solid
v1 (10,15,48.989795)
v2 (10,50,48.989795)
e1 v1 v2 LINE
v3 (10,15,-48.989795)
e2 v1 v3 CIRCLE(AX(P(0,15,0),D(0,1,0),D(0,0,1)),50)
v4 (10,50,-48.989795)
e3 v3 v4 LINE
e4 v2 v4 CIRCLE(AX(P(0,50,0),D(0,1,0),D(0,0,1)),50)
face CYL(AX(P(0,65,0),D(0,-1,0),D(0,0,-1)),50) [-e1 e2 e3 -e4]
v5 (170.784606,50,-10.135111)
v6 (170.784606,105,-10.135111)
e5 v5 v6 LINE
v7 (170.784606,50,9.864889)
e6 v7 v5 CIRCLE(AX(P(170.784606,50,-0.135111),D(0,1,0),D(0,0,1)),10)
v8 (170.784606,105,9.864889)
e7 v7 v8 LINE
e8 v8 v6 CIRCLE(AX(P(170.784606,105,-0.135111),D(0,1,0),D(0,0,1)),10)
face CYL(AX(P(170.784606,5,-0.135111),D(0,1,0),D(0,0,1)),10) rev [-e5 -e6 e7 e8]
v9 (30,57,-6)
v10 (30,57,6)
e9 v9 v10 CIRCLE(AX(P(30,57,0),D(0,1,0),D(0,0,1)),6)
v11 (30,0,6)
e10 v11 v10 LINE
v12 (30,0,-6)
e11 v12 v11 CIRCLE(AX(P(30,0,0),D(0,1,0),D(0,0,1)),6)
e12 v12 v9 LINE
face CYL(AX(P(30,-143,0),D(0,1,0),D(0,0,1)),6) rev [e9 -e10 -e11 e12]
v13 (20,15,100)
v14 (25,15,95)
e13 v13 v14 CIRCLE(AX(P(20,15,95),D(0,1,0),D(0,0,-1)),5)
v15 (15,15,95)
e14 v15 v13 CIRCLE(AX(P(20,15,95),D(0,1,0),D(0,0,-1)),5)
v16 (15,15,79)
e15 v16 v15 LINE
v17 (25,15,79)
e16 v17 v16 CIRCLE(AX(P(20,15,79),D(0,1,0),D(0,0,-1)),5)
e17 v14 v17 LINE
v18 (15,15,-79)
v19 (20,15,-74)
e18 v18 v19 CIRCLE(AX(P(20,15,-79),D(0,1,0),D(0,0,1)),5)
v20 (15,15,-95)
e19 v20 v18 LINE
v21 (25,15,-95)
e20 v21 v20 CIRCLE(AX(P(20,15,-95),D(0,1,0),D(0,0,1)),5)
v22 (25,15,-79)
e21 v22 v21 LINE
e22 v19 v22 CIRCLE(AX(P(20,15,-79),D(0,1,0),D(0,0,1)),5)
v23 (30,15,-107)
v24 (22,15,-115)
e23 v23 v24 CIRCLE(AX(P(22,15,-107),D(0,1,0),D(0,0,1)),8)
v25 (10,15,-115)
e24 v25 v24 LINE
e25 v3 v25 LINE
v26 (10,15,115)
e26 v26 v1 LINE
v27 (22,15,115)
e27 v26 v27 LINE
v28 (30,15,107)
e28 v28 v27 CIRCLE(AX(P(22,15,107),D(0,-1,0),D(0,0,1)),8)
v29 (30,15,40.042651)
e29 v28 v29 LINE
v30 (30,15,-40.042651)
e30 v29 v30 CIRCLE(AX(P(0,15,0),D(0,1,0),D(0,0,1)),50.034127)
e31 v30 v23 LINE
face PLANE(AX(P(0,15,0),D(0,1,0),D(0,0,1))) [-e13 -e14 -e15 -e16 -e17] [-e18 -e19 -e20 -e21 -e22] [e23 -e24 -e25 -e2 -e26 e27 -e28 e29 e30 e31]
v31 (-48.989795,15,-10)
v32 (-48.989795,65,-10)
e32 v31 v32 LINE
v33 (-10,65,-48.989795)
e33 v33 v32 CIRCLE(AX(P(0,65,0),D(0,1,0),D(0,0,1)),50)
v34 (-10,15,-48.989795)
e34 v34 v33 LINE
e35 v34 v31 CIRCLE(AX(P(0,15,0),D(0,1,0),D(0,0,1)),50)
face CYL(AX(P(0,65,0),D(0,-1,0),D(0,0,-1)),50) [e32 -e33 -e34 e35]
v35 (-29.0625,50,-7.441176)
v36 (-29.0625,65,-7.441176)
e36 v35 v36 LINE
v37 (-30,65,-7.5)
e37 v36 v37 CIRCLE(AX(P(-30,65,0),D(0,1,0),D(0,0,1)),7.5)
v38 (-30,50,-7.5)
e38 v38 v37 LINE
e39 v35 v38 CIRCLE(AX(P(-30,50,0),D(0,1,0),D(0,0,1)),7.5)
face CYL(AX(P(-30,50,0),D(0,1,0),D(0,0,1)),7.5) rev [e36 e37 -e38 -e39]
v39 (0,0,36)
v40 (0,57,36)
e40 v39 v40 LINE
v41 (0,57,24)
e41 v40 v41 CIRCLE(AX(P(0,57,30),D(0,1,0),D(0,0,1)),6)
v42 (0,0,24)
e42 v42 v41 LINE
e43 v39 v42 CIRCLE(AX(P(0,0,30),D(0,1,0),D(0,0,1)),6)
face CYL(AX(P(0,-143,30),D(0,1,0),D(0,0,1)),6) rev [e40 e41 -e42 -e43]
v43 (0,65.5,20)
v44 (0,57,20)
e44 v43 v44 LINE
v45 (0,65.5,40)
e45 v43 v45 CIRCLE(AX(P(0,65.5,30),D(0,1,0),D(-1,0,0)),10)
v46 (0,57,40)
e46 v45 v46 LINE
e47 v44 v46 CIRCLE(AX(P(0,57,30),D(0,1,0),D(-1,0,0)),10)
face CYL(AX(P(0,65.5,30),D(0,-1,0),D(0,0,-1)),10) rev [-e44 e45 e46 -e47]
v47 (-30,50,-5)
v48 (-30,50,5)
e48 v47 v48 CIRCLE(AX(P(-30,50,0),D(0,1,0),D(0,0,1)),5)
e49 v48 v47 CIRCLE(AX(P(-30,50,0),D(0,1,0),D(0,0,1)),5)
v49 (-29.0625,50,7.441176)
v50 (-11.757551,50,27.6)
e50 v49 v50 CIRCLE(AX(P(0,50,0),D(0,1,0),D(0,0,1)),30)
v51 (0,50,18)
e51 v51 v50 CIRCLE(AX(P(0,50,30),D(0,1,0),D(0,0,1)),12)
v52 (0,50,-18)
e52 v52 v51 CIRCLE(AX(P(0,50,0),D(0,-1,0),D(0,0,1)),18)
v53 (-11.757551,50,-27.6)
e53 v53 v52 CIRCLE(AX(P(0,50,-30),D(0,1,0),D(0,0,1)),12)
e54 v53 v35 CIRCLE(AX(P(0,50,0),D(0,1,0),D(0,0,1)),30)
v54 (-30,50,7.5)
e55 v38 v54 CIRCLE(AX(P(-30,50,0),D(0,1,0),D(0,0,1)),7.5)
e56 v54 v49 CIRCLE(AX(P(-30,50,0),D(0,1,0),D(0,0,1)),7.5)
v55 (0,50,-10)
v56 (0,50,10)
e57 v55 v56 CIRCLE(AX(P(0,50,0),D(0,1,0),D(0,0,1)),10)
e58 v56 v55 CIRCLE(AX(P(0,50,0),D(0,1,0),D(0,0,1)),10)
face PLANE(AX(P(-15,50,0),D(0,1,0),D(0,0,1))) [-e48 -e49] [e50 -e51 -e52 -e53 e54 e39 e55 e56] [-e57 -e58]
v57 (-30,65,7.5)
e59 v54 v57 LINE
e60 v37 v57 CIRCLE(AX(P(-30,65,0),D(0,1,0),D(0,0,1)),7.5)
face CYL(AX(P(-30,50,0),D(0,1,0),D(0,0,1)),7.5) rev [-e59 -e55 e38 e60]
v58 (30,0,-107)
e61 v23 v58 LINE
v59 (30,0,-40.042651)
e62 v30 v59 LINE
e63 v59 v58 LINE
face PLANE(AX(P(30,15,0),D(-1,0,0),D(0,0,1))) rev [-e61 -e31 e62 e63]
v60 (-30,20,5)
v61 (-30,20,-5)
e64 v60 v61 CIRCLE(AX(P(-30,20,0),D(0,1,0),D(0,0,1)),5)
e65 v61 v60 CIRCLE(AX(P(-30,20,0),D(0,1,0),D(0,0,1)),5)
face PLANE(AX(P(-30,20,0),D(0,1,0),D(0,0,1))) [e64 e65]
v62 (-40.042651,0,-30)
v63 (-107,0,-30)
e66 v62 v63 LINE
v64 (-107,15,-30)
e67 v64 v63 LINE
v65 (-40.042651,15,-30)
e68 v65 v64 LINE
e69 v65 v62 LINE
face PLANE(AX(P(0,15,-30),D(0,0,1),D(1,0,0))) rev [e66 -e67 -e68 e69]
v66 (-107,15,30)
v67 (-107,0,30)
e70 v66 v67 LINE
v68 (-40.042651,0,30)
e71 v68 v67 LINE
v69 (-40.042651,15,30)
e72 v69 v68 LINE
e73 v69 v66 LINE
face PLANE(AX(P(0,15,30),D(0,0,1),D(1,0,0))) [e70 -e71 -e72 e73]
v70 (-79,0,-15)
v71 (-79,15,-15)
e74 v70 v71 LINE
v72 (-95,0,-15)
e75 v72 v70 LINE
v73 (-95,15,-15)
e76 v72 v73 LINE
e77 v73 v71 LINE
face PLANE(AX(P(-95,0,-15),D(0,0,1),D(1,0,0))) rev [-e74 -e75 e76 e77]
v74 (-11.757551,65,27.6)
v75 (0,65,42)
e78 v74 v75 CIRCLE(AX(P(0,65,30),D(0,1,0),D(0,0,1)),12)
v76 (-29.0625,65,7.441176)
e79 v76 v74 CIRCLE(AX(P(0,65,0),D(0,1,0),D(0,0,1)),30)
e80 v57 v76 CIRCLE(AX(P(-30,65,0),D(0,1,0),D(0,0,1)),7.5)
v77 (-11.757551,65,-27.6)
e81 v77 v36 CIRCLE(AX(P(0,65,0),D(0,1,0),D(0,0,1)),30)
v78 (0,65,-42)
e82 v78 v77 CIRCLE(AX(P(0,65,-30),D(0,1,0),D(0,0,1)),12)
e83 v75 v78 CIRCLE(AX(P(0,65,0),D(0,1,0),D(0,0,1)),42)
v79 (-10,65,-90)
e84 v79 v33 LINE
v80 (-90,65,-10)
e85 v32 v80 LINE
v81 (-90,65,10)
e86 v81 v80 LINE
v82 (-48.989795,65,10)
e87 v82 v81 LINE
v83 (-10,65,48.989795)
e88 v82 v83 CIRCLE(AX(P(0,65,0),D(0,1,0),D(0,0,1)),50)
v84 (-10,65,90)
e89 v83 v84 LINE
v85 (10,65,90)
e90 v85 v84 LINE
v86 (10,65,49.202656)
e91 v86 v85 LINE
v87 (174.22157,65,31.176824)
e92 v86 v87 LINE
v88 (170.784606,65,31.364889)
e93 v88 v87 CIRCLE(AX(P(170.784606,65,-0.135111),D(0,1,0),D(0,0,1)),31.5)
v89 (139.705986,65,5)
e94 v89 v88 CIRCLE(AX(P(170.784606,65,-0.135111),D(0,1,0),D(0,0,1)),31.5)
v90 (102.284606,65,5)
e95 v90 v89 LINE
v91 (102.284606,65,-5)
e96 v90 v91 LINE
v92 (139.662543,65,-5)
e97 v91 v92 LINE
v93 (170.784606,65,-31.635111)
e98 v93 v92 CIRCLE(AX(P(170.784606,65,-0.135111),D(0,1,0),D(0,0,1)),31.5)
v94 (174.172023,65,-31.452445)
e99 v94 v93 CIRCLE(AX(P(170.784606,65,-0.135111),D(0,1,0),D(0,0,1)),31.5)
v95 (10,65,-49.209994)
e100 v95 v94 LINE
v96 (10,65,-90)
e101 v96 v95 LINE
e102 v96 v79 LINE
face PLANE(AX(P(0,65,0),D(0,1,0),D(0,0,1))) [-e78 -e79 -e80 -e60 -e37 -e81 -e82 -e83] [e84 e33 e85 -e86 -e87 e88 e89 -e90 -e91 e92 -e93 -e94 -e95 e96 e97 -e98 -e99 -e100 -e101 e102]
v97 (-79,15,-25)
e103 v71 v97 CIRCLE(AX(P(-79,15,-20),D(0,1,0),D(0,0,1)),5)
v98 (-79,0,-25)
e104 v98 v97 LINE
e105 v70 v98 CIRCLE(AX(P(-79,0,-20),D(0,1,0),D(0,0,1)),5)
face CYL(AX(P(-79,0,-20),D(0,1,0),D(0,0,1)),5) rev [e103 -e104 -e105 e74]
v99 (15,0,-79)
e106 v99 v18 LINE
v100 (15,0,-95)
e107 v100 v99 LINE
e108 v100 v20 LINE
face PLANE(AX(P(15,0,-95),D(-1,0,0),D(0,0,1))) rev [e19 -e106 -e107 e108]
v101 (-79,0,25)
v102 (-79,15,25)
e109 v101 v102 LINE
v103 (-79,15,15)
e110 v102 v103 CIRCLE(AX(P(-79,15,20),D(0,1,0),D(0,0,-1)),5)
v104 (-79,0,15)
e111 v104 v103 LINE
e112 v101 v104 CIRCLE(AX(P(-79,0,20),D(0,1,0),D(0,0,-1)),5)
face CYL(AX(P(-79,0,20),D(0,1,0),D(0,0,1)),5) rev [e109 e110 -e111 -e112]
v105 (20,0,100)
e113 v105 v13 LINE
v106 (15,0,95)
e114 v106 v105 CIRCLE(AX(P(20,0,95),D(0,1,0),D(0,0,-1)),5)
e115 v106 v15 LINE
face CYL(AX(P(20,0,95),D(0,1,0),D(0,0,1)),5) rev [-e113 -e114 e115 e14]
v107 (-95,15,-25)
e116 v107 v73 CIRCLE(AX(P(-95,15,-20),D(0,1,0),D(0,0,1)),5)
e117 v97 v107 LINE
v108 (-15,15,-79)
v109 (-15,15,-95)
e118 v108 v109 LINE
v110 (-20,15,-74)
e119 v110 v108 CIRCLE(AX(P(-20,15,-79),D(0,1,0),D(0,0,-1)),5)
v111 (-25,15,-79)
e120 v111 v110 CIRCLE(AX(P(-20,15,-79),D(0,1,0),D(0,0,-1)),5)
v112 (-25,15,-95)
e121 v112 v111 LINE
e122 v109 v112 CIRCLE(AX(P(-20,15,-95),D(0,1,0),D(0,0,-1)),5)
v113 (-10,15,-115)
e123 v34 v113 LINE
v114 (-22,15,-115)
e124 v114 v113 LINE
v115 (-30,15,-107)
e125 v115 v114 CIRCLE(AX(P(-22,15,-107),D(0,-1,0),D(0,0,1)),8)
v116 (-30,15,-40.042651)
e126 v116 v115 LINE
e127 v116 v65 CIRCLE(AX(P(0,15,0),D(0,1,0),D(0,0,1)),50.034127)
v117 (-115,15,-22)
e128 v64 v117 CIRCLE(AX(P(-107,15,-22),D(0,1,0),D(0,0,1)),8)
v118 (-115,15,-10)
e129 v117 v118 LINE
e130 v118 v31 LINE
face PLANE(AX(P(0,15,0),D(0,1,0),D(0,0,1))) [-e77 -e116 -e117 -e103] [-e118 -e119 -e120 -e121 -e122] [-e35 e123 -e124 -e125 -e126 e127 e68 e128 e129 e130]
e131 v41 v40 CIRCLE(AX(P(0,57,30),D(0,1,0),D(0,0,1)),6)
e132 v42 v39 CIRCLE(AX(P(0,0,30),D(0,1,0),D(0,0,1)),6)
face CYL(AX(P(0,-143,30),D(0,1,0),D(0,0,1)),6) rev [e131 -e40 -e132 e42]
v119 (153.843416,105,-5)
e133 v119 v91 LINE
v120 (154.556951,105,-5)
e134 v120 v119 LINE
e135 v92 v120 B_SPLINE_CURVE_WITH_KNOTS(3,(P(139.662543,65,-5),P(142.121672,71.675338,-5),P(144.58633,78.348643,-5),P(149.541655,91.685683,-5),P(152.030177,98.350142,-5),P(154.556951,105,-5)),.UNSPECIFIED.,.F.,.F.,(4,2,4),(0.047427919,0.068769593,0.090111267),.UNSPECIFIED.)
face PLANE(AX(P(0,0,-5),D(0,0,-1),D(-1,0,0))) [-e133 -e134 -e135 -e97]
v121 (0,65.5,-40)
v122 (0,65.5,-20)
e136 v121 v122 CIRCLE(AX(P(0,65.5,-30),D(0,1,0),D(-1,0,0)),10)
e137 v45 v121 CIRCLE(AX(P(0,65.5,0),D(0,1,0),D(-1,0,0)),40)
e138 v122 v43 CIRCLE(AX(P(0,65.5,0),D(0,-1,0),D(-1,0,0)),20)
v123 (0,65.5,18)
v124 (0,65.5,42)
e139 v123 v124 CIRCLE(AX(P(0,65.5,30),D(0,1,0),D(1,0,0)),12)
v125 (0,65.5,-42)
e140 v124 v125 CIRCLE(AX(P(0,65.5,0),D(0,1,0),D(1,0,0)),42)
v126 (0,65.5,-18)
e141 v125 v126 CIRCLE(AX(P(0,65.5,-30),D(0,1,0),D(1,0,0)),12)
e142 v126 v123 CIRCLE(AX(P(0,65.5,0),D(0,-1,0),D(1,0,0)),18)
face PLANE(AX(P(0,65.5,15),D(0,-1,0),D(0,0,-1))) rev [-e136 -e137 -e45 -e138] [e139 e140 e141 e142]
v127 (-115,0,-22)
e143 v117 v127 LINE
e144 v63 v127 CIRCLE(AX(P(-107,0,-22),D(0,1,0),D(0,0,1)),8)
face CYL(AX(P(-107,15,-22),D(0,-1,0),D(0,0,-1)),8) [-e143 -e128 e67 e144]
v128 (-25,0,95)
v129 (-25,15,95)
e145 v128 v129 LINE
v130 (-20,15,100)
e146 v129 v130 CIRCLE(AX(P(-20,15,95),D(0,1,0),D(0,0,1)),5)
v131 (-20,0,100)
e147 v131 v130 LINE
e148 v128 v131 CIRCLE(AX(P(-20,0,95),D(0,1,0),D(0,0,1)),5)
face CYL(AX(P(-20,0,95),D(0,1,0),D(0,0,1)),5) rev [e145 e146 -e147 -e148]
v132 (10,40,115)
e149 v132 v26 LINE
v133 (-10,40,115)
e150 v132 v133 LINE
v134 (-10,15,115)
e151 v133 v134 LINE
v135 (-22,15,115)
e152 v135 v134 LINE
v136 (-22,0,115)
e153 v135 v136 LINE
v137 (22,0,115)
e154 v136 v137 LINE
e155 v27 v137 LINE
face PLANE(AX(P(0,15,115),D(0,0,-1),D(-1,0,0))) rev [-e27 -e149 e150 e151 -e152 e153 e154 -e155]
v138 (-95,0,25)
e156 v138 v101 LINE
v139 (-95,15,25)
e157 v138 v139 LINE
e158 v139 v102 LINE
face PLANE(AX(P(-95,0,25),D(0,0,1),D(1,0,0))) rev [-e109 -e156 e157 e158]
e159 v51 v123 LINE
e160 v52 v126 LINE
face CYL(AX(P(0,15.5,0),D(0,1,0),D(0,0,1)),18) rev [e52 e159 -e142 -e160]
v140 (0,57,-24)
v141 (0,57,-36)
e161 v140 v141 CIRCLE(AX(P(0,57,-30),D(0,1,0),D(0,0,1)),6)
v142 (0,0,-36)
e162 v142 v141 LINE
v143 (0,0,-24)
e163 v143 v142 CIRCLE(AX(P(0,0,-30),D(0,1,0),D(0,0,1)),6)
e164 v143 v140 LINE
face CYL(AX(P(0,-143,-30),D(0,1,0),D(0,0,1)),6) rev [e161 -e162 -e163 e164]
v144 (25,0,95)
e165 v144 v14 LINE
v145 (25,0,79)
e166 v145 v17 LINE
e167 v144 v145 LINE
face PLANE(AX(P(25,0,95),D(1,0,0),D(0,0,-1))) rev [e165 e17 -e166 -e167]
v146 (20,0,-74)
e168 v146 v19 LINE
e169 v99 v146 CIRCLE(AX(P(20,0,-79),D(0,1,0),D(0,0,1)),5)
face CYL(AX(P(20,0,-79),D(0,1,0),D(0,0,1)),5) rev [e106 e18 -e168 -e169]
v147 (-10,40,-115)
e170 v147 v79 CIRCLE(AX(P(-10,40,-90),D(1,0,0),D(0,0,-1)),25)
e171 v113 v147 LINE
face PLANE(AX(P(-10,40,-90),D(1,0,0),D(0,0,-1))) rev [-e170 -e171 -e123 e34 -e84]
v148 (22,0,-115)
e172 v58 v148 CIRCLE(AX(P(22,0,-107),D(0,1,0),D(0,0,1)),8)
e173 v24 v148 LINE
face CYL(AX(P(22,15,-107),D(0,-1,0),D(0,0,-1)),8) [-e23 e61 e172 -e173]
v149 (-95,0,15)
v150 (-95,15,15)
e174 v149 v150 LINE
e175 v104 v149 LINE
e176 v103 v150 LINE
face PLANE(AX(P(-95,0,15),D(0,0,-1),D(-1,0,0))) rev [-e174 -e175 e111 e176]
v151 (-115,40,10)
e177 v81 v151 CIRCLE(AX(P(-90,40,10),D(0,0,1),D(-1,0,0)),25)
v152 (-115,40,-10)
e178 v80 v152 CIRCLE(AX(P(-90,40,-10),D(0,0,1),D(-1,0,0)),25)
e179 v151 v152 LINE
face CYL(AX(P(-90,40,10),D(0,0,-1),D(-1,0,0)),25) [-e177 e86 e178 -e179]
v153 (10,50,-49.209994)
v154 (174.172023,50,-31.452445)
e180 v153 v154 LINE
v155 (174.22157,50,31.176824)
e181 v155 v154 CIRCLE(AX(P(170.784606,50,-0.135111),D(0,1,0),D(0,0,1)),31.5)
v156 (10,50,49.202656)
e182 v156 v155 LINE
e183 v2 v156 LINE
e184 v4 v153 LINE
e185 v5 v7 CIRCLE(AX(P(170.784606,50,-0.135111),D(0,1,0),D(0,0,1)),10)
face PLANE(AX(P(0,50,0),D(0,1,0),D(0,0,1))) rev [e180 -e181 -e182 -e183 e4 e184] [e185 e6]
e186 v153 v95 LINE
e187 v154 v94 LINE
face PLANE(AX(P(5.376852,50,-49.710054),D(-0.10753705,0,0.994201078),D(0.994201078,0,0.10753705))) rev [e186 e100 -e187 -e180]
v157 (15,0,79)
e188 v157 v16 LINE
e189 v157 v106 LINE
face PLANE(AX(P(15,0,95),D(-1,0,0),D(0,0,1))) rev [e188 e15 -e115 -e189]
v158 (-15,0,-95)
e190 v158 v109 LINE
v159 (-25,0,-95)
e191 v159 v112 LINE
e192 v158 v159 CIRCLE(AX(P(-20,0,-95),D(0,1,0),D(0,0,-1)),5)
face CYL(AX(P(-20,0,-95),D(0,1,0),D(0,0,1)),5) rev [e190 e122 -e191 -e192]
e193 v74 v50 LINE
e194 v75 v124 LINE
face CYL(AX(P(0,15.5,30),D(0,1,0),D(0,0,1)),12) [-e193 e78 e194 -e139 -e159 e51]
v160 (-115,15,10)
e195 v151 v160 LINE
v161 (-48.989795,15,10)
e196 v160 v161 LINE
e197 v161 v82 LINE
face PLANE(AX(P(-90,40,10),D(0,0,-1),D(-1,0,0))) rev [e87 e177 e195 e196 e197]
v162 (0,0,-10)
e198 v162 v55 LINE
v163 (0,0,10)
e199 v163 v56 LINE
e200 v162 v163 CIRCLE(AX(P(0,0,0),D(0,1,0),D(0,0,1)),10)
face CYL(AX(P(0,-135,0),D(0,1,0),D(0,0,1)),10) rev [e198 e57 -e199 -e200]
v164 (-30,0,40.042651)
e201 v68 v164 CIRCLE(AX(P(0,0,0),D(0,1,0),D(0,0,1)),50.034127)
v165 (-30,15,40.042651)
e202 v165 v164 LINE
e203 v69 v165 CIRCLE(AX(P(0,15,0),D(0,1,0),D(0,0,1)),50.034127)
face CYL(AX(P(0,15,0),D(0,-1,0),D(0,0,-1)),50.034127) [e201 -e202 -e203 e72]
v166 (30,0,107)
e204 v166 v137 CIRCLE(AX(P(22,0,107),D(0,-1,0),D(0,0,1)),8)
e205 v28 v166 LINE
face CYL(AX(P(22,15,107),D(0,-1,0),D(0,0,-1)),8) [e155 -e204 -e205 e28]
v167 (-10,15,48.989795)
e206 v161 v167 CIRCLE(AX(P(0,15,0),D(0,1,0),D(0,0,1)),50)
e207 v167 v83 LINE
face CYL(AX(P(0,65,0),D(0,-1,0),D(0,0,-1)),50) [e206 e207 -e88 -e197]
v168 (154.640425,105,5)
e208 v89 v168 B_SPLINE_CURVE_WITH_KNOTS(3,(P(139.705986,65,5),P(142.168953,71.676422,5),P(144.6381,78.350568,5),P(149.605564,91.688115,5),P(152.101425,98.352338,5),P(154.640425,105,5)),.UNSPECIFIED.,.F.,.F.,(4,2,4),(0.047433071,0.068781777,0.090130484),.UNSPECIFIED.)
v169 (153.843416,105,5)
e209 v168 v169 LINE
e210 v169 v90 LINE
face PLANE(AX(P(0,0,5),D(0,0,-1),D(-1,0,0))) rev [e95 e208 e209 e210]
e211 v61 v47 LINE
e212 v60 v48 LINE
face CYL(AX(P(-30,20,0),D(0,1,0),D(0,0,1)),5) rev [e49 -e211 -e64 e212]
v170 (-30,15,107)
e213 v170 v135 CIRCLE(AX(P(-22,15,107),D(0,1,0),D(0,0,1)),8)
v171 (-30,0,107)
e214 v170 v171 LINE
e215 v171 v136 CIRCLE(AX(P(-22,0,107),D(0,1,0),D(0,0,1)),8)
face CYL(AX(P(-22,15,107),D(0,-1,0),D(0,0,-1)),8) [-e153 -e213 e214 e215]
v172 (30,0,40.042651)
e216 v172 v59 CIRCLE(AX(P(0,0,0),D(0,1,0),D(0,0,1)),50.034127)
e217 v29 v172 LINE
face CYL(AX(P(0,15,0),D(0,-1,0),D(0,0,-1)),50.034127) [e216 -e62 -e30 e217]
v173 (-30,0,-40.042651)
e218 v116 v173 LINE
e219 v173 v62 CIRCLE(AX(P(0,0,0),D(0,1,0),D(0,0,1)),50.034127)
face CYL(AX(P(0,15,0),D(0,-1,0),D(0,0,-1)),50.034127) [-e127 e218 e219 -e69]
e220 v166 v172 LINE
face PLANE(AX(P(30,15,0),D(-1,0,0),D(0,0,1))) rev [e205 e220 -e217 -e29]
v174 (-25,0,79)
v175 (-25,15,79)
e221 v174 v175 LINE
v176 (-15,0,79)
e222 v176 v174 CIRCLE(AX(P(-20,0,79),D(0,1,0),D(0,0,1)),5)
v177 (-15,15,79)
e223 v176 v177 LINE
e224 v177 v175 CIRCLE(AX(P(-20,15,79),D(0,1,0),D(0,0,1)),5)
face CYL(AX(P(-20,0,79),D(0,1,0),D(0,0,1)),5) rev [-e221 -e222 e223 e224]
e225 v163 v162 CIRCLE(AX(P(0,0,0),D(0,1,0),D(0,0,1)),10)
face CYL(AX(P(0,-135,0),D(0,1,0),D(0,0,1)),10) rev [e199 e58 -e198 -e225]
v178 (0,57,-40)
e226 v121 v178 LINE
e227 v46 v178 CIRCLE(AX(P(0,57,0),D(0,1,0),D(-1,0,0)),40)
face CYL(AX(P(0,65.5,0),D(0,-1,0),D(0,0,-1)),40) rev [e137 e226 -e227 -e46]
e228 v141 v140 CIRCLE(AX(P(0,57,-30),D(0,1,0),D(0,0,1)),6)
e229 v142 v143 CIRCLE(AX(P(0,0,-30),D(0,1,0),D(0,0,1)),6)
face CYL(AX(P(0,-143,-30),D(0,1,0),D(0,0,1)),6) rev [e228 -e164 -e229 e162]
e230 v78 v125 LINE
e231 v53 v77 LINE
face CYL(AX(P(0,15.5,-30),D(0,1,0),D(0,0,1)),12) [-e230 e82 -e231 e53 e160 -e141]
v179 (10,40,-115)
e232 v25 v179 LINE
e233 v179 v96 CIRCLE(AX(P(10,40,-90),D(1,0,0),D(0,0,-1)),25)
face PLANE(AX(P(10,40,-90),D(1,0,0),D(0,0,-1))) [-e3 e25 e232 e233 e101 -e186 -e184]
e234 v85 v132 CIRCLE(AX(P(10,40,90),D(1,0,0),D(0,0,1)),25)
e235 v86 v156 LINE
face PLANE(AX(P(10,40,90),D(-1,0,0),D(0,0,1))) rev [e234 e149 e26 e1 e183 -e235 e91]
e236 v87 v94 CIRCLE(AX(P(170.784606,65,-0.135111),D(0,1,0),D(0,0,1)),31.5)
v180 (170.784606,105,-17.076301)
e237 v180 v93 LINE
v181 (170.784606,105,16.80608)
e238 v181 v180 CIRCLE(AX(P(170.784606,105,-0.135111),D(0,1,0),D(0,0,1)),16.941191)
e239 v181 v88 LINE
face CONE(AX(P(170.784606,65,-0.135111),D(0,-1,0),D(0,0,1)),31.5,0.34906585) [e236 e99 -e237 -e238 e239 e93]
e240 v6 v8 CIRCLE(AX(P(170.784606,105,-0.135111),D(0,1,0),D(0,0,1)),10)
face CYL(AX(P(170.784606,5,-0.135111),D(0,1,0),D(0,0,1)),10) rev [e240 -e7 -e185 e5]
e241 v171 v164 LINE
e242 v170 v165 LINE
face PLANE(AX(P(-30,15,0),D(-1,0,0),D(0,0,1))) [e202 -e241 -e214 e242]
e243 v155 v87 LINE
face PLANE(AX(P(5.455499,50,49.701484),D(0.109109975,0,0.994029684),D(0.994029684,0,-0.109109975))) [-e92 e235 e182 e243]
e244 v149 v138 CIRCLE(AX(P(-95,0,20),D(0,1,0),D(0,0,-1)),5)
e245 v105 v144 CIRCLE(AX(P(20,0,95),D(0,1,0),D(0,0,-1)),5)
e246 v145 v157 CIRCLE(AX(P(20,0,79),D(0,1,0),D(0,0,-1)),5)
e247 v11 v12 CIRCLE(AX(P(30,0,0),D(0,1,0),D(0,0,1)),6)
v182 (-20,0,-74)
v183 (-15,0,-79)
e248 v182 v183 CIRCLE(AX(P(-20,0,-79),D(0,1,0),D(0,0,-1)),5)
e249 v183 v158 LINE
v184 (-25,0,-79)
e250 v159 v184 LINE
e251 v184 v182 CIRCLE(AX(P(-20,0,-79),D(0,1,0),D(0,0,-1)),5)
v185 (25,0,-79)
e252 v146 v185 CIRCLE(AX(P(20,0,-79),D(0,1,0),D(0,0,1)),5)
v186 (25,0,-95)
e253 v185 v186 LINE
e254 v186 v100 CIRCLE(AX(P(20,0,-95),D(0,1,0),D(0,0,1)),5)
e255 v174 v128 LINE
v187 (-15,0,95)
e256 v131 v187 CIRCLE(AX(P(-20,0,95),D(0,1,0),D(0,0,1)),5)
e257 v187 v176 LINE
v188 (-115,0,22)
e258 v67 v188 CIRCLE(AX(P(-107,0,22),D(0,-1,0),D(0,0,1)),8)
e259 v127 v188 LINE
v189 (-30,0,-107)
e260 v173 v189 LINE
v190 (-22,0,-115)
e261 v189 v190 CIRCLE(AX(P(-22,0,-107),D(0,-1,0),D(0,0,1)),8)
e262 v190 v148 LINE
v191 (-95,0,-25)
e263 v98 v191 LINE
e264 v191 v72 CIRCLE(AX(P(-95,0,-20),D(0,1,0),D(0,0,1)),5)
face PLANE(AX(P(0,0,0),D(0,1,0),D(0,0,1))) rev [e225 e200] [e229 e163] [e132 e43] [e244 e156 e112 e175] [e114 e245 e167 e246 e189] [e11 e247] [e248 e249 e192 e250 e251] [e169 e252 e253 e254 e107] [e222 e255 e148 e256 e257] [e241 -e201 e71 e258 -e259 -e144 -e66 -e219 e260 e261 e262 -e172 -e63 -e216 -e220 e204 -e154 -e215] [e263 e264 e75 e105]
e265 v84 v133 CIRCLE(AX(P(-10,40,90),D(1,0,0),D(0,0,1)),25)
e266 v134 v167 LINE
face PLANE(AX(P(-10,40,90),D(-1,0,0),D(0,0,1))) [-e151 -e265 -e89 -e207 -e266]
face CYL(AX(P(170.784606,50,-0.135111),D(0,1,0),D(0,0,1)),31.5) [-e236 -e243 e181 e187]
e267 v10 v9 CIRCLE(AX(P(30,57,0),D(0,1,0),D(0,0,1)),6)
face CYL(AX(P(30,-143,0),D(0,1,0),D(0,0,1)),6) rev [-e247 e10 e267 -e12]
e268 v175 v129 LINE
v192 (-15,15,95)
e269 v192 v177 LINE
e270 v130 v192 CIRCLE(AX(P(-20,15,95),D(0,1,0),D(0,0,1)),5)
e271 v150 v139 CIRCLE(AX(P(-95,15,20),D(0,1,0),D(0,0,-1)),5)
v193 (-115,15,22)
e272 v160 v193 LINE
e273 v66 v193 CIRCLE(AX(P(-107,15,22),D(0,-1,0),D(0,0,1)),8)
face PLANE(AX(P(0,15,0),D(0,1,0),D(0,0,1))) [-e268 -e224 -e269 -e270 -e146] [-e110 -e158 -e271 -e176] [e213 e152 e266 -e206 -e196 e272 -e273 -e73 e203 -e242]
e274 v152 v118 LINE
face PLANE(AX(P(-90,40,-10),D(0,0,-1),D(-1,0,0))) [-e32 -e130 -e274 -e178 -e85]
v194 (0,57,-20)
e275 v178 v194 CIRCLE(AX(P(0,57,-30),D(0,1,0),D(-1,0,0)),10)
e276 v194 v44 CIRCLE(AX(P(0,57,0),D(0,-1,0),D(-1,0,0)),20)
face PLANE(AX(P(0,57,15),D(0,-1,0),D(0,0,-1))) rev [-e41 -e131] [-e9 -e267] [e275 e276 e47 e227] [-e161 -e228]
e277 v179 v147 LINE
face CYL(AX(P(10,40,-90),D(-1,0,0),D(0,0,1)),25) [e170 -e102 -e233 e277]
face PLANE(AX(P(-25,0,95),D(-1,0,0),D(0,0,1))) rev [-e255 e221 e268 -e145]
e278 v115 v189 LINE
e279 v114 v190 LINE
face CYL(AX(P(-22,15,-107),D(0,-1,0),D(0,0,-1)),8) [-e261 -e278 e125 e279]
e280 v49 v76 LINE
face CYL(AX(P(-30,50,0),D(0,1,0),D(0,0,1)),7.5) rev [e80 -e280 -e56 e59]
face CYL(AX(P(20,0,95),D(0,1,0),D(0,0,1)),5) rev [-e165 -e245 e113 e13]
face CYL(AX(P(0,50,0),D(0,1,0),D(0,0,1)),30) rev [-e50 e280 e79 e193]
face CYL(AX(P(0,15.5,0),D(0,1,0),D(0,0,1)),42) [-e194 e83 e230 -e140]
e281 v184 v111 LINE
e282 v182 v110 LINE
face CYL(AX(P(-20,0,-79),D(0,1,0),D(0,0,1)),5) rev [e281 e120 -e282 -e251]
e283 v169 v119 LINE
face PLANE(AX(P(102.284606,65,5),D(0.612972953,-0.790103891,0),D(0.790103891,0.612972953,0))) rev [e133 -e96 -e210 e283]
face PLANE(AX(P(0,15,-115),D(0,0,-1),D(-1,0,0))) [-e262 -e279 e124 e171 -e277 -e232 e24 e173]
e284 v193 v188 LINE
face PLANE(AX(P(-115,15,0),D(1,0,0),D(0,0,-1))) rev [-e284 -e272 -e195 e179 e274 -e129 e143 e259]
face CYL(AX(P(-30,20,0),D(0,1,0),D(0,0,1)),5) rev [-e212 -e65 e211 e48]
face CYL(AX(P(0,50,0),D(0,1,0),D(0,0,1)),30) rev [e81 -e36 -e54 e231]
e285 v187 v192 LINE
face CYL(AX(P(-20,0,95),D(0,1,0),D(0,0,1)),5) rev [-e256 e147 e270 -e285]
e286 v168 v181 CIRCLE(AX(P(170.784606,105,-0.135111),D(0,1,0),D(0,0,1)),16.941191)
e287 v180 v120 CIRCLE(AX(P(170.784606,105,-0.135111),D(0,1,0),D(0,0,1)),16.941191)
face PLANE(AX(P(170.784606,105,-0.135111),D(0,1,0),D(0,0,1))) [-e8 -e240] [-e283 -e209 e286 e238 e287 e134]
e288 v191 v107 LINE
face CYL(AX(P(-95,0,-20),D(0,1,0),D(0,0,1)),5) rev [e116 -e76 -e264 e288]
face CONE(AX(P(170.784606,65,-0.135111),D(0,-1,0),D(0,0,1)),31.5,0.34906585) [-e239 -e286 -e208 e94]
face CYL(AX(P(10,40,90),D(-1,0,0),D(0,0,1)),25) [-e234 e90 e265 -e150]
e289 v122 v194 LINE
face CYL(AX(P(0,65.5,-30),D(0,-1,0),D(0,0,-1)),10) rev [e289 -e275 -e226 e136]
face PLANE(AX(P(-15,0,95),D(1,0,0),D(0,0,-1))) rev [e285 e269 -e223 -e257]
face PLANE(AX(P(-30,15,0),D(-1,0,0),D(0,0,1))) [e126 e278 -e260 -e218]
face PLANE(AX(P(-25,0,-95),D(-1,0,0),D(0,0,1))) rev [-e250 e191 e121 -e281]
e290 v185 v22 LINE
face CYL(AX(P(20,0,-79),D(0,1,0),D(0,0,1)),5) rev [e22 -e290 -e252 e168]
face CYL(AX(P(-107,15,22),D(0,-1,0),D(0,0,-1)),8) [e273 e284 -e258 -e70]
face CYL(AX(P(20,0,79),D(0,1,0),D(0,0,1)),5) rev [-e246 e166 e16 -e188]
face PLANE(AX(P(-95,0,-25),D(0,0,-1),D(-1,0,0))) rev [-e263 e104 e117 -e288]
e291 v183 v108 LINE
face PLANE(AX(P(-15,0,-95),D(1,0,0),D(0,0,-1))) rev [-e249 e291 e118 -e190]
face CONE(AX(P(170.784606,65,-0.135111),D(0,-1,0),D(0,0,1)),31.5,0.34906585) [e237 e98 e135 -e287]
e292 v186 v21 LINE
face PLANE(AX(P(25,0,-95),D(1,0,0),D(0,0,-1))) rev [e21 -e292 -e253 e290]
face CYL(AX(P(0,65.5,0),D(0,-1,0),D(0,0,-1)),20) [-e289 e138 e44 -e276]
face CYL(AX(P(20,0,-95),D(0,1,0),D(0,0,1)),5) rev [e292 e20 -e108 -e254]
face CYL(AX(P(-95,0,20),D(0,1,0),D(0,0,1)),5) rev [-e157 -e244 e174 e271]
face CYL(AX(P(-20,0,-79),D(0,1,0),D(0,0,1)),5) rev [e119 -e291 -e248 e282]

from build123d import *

# Parameters (mm, degrees)
CROSS_BASE_PLATE_SKETCH_R    = 50.034127187
CROSS_BASE_PLATE_DEPTH       = 15
ARM_SLOTS_DEPTH              = 15
CENTRAL_HUB_SKETCH_R         = 50
CENTRAL_HUB_100_DEPTH        = 50
TRUNNION_START               = -15
TRUNNION_ARM_PLATE_DEPTH     = 15
TRUNNION_CONE_SKETCH_R       = 31.5
TRUNNION_CONE_BOSS_DEPTH     = 40
TRUNNION_CONE_BOSS_TAPER     = 20
TRUNNION_BORE_SKETCH_R       = 10
TRUNNION_BORE_20_DEPTH       = 100
TRUNNION_GUSSET_DEPTH        = 5
ARM_UPRIGHT_BLOCK_DEPTH      = 10
ARM_UPRIGHT_BLOCK_PAIR_DEPTH = 10
CENTRAL_BORE_SKETCH_R        = 10
CENTRAL_BORE_20_DEPTH        = 200
HUB_TOP_RECESS_SKETCH_R      = 10
HUB_TOP_RECESS_DEPTH         = 15
HUB_LOBE_POCKET_DEPTH        = 8
POCKET_FLOOR_PAD_DEPTH       = 1
POCKET_START                 = 8.5
POCKET_THIN_WALL_DEPTH       = 8.5
HUB_PIN_HOLES_SKETCH_R       = 6
HUB_PIN_HOLES_DEPTH          = 200
POCKET_OUTER_WALL_DEPTH      = 50
PIN_HOLE_BOSSES_SKETCH_R     = 6
PIN_HOLE_BOSSES_DEPTH        = 20
HUB_SIDE_HOLE_SKETCH_R       = 5
HUB_SIDE_HOLE_10_DEPTH       = 30


with BuildPart() as part:
    # Cross Base Plate Sketch → Cross Base Plate (new body)
    with BuildSketch(Plane(origin=(0, 0, 0), x_dir=(1, 0, 0), z_dir=(0, 1, 0))):
        with BuildLine():
            ThreePointArc((-40.042650803, -30), (-50.034127187, 0), (-40.042650803, 30))
            Line((-40.042650803, 30), (-107, 30))
            ThreePointArc((-107, 30), (-112.656854249, 27.656854249), (-115, 22))
            Line((-115, 22), (-115, -22))
            ThreePointArc((-115, -22), (-112.656854249, -27.656854249), (-107, -30))
            Line((-107, -30), (-40.042650803, -30))
        make_face()
        Circle(CROSS_BASE_PLATE_SKETCH_R)
        with BuildLine():
            ThreePointArc((-30, 40.042650803), (0, 50.034127187), (30, 40.042650803))
            Line((30, 40.042650803), (30, 107))
            ThreePointArc((30, 107), (27.656854249, 112.656854249), (22, 115))
            Line((22, 115), (-22, 115))
            ThreePointArc((-22, 115), (-27.656854249, 112.656854249), (-30, 107))
            Line((-30, 107), (-30, 40.042650803))
        make_face()
        with BuildLine():
            Line((30, -107), (30, -40.042650803))
            ThreePointArc((30, -40.042650803), (0, -50.034127187), (-30, -40.042650803))
            Line((-30, -40.042650803), (-30, -107))
            ThreePointArc((-30, -107), (-27.656854249, -112.656854249), (-22, -115))
            Line((-22, -115), (22, -115))
            ThreePointArc((22, -115), (27.656854249, -112.656854249), (30, -107))
        make_face()
    extrude(amount=CROSS_BASE_PLATE_DEPTH)

    # Arm Slots Sketch → Arm Slots (cut)
    with BuildSketch(Plane(origin=(0, 15, 0), x_dir=(1, 0, 0), z_dir=(0, 1, 0))):
        with BuildLine():
            Line((-95, 25), (-79, 25))
            ThreePointArc((-79, 25), (-74, 20), (-79, 15))
            Line((-79, 15), (-95, 15))
            ThreePointArc((-95, 15), (-100, 20), (-95, 25))
        make_face()
        with BuildLine():
            Line((-95, -25), (-79, -25))
            ThreePointArc((-79, -25), (-74, -20), (-79, -15))
            Line((-79, -15), (-95, -15))
            ThreePointArc((-95, -15), (-100, -20), (-95, -25))
        make_face()
        with BuildLine():
            Line((25, 95), (25, 79))
            ThreePointArc((25, 79), (20, 74), (15, 79))
            Line((15, 79), (15, 95))
            ThreePointArc((15, 95), (20, 100), (25, 95))
        make_face()
        with BuildLine():
            Line((-25, 95), (-25, 79))
            ThreePointArc((-25, 79), (-20, 74), (-15, 79))
            Line((-15, 79), (-15, 95))
            ThreePointArc((-15, 95), (-20, 100), (-25, 95))
        make_face()
        with BuildLine():
            Line((25, -95), (25, -79))
            ThreePointArc((25, -79), (20, -74), (15, -79))
            Line((15, -79), (15, -95))
            ThreePointArc((15, -95), (20, -100), (25, -95))
        make_face()
        with BuildLine():
            Line((-25, -95), (-25, -79))
            ThreePointArc((-25, -79), (-20, -74), (-15, -79))
            Line((-15, -79), (-15, -95))
            ThreePointArc((-15, -95), (-20, -100), (-25, -95))
        make_face()
    extrude(amount=-ARM_SLOTS_DEPTH, mode=Mode.SUBTRACT)

    # Central Hub Sketch → Central Hub Ø100 (add)
    with BuildSketch(Plane(origin=(0, 15, 0), x_dir=(1, 0, 0), z_dir=(0, 1, 0))):
        with Locations(Location((0, 0, 0), (0, 0, 270))):
            Circle(CENTRAL_HUB_SKETCH_R)
    extrude(amount=CENTRAL_HUB_100_DEPTH)

    # Trunnion Arm Plate Sketch → Trunnion Arm Plate (add)
    with BuildSketch(Plane(origin=(0, 65, 0), x_dir=(1, 0, 0), z_dir=(0, 1, 0)).offset(TRUNNION_START)):
        with BuildLine():
            Line((174.172023337, 31.452444757), (5.376852484, 49.710053886))
            ThreePointArc((5.376852484, 49.710053886), (37.207812514, 33.400279758), (50, 0))
            ThreePointArc((50, 0), (37.234224431, -33.370833538), (5.45549876, -49.701484216))
            Line((5.45549876, -49.701484216), (174.221570491, -31.176824248))
            ThreePointArc((174.221570491, -31.176824248), (202.284596415, 0.160031023), (174.172023337, 31.452444757))
        make_face()
    extrude(amount=TRUNNION_ARM_PLATE_DEPTH)

    # Trunnion Cone Sketch → Trunnion Cone Boss (add)
    with BuildSketch(Plane(origin=(0, 65, 0), x_dir=(1, 0, 0), z_dir=(0, 1, 0))):
        with Locations((170.784606272, 0.135110808)):
            Circle(TRUNNION_CONE_SKETCH_R)
    extrude(amount=TRUNNION_CONE_BOSS_DEPTH, taper=TRUNNION_CONE_BOSS_TAPER)

    # Trunnion Bore Sketch → Trunnion Bore Ø20 (cut)
    with BuildSketch(Plane(origin=(0, 105, 0), x_dir=(1, 0, 0), z_dir=(0, 1, 0))):
        with Locations(Location((170.784606272, 0.135110808, 0), (0, 0, 270))):
            Circle(TRUNNION_BORE_SKETCH_R)
    extrude(amount=-TRUNNION_BORE_20_DEPTH, mode=Mode.SUBTRACT)

    # Trunnion Gusset Sketch → Trunnion Gusset (add, symmetric)
    with BuildSketch(Plane.XY):
        Polygon((158.843415643, 65), (102.284606272, 65), (153.843415643, 105), (158.843415643, 105), align=None)
    extrude(amount=TRUNNION_GUSSET_DEPTH, both=True)

    # Arm Upright Block Sketch → Arm Upright Block (add, symmetric)
    with BuildSketch(Plane.XY):
        with BuildLine():
            Line((-115, 15), (-115, 30))
            Line((-115, 30), (-115, 40))
            ThreePointArc((-115, 40), (-107.67766953, 57.67766953), (-90, 65))
            Line((-90, 65), (-42.455555727, 65))
            Line((-42.455555727, 65), (-42.455555727, 15))
            Line((-42.455555727, 15), (-115, 15))
        make_face()
    extrude(amount=ARM_UPRIGHT_BLOCK_DEPTH, both=True)

    # Arm Upright Block Pair Sketch → Arm Upright Block Pair (add, symmetric)
    with BuildSketch(Plane(origin=(0, 0, 0), x_dir=(0, 0, -1), z_dir=(1, 0, 0))):
        with BuildLine():
            Line((115, 15), (115, 40))
            ThreePointArc((115, 40), (107.67766953, 57.67766953), (90, 65))
            Line((90, 65), (40.208016437, 65))
            Line((40.208016437, 65), (40.042650803, 15))
            Line((40.042650803, 15), (115, 15))
        make_face()
        with BuildLine():
            Line((-115, 15), (-115, 40))
            ThreePointArc((-115, 40), (-107.67766953, 57.67766953), (-90, 65))
            Line((-90, 65), (-41.408255734, 65))
            Line((-41.408255734, 65), (-41.408255734, 15))
            Line((-41.408255734, 15), (-115, 15))
        make_face()
    extrude(amount=ARM_UPRIGHT_BLOCK_PAIR_DEPTH, both=True)

    # Central Bore Sketch → Central Bore Ø20 (cut)
    with BuildSketch(Plane(origin=(0, 65, 0), x_dir=(1, 0, 0), z_dir=(0, 1, 0))):
        with Locations(Location((0, 0, 0), (0, 0, 270))):
            Circle(CENTRAL_BORE_SKETCH_R)
    extrude(amount=-CENTRAL_BORE_20_DEPTH, mode=Mode.SUBTRACT)

    # Hub Top Recess Sketch → Hub Top Recess (cut)
    with BuildSketch(Plane(origin=(0, 65, 0), x_dir=(1, 0, 0), z_dir=(0, 1, 0))):
        with BuildLine():
            ThreePointArc((-29.0625, -7.441175562), (30, 0), (-29.0625, 7.441175562))
            ThreePointArc((-29.0625, 7.441175562), (-37.5, 0), (-29.0625, -7.441175562))
        make_face()
        with Locations(Location((0, 0, 0), (0, 0, 270))):
            Circle(HUB_TOP_RECESS_SKETCH_R, mode=Mode.SUBTRACT)
    extrude(amount=-HUB_TOP_RECESS_DEPTH, mode=Mode.SUBTRACT)

    # Hub Lobe Pocket Sketch → Hub Lobe Pocket (cut)
    with BuildSketch(Plane(origin=(0, 65, 0), x_dir=(1, 0, 0), z_dir=(0, 1, 0))):
        with BuildLine():
            ThreePointArc((0, 41), (-11, 30), (0, 19))
            ThreePointArc((0, 19), (19, 0), (0, -19))
            ThreePointArc((0, -19), (-11, -30), (0, -41))
            ThreePointArc((0, -41), (41, 0), (0, 41))
        make_face()
    extrude(amount=-HUB_LOBE_POCKET_DEPTH, mode=Mode.SUBTRACT)

    # Pocket Floor Pad Sketch → Pocket Floor Pad (add)
    with BuildSketch(Plane(origin=(0, 57, 0), x_dir=(1, 0, 0), z_dir=(0, 1, 0))):
        with BuildLine():
            ThreePointArc((0, 41), (-11, 30), (0, 19))
            ThreePointArc((0, 19), (19, 0), (0, -19))
            ThreePointArc((0, -19), (-11, -30), (0, -41))
            ThreePointArc((0, -41), (41, 0), (0, 41))
        make_face()
    extrude(amount=-POCKET_FLOOR_PAD_DEPTH)

    # Pocket Thin Wall Sketch → Pocket Thin Wall (add)
    with BuildSketch(Plane(origin=(0, 57, 0), x_dir=(1, 0, 0), z_dir=(0, 1, 0)).offset(POCKET_START)):
        with BuildLine():
            ThreePointArc((0, 41), (-11, 30), (0, 19))
            ThreePointArc((0, 19), (19, 0), (0, -19))
            ThreePointArc((0, -19), (-11, -30), (0, -41))
            ThreePointArc((0, -41), (41, 0), (0, 41))
        make_face()
        with BuildLine():
            ThreePointArc((0, 40), (-10, 30), (0, 20))
            ThreePointArc((0, 20), (20, 0), (0, -20))
            ThreePointArc((0, -20), (-10, -30), (0, -40))
            ThreePointArc((0, -40), (40, 0), (0, 40))
        make_face(mode=Mode.SUBTRACT)
    extrude(amount=-POCKET_THIN_WALL_DEPTH)

    # Hub Pin Holes Sketch → Hub Pin Holes (cut)
    with BuildSketch(Plane(origin=(0, 57, 0), x_dir=(1, 0, 0), z_dir=(0, 1, 0))):
        with Locations(Location((0, 30, 0), (0, 0, 270))):
            Circle(HUB_PIN_HOLES_SKETCH_R)
        with Locations(Location((30, 0, 0), (0, 0, 270))):
            Circle(HUB_PIN_HOLES_SKETCH_R)
        with Locations(Location((0, -30, 0), (0, 0, 270))):
            Circle(HUB_PIN_HOLES_SKETCH_R)
    extrude(amount=-HUB_PIN_HOLES_DEPTH, mode=Mode.SUBTRACT)

    # Pocket Outer Wall Sketch → Pocket Outer Wall (add)
    with BuildSketch(Plane(origin=(0, 65.5, 0), x_dir=(1, 0, 0), z_dir=(0, 1, 0))):
        with BuildLine():
            ThreePointArc((0, 18), (18, 0), (0, -18))
            ThreePointArc((0, -18), (-12, -30), (0, -42))
            ThreePointArc((0, -42), (42, 0), (0, 42))
            ThreePointArc((0, 42), (-12, 30), (0, 18))
        make_face()
        with BuildLine():
            ThreePointArc((0, 19), (19, 0), (0, -19))
            ThreePointArc((0, -19), (-11, -30), (0, -41))
            ThreePointArc((0, -41), (41, 0), (0, 41))
            ThreePointArc((0, 41), (-11, 30), (0, 19))
        make_face(mode=Mode.SUBTRACT)
    extrude(amount=-POCKET_OUTER_WALL_DEPTH)

    # Pin Hole Bosses Sketch → Pin Hole Bosses (add)
    with BuildSketch(Plane(origin=(0, 57, 0), x_dir=(1, 0, 0), z_dir=(0, 1, 0))):
        with BuildLine():
            ThreePointArc((-10.777754868, -27.8), (-8.520563362, -36.957010852), (0, -41))
            ThreePointArc((0, -41), (41, 0), (0, 41))
            ThreePointArc((0, 41), (-11, 30), (0, 19))
            ThreePointArc((0, 19), (19, 0), (0, -19))
            ThreePointArc((0, -19), (-6.957010852, -21.479436638), (-10.777754868, -27.8))
        make_face()
        with Locations(Location((0, 30, 0), (0, 0, 270))):
            Circle(PIN_HOLE_BOSSES_SKETCH_R, mode=Mode.SUBTRACT)
        with Locations(Location((30, 0, 0), (0, 0, 270))):
            Circle(PIN_HOLE_BOSSES_SKETCH_R, mode=Mode.SUBTRACT)
        with Locations(Location((0, -30, 0), (0, 0, 270))):
            Circle(PIN_HOLE_BOSSES_SKETCH_R, mode=Mode.SUBTRACT)
    extrude(amount=-PIN_HOLE_BOSSES_DEPTH)

    # Hub Side Hole Sketch → Hub Side Hole Ø10 (cut)
    with BuildSketch(Plane(origin=(0, 50, 0), x_dir=(1, 0, 0), z_dir=(0, 1, 0))):
        with Locations(Location((-30, 0, 0), (0, 0, 270))):
            Circle(HUB_SIDE_HOLE_SKETCH_R)
    extrude(amount=-HUB_SIDE_HOLE_10_DEPTH, mode=Mode.SUBTRACT)


solid = part.part
